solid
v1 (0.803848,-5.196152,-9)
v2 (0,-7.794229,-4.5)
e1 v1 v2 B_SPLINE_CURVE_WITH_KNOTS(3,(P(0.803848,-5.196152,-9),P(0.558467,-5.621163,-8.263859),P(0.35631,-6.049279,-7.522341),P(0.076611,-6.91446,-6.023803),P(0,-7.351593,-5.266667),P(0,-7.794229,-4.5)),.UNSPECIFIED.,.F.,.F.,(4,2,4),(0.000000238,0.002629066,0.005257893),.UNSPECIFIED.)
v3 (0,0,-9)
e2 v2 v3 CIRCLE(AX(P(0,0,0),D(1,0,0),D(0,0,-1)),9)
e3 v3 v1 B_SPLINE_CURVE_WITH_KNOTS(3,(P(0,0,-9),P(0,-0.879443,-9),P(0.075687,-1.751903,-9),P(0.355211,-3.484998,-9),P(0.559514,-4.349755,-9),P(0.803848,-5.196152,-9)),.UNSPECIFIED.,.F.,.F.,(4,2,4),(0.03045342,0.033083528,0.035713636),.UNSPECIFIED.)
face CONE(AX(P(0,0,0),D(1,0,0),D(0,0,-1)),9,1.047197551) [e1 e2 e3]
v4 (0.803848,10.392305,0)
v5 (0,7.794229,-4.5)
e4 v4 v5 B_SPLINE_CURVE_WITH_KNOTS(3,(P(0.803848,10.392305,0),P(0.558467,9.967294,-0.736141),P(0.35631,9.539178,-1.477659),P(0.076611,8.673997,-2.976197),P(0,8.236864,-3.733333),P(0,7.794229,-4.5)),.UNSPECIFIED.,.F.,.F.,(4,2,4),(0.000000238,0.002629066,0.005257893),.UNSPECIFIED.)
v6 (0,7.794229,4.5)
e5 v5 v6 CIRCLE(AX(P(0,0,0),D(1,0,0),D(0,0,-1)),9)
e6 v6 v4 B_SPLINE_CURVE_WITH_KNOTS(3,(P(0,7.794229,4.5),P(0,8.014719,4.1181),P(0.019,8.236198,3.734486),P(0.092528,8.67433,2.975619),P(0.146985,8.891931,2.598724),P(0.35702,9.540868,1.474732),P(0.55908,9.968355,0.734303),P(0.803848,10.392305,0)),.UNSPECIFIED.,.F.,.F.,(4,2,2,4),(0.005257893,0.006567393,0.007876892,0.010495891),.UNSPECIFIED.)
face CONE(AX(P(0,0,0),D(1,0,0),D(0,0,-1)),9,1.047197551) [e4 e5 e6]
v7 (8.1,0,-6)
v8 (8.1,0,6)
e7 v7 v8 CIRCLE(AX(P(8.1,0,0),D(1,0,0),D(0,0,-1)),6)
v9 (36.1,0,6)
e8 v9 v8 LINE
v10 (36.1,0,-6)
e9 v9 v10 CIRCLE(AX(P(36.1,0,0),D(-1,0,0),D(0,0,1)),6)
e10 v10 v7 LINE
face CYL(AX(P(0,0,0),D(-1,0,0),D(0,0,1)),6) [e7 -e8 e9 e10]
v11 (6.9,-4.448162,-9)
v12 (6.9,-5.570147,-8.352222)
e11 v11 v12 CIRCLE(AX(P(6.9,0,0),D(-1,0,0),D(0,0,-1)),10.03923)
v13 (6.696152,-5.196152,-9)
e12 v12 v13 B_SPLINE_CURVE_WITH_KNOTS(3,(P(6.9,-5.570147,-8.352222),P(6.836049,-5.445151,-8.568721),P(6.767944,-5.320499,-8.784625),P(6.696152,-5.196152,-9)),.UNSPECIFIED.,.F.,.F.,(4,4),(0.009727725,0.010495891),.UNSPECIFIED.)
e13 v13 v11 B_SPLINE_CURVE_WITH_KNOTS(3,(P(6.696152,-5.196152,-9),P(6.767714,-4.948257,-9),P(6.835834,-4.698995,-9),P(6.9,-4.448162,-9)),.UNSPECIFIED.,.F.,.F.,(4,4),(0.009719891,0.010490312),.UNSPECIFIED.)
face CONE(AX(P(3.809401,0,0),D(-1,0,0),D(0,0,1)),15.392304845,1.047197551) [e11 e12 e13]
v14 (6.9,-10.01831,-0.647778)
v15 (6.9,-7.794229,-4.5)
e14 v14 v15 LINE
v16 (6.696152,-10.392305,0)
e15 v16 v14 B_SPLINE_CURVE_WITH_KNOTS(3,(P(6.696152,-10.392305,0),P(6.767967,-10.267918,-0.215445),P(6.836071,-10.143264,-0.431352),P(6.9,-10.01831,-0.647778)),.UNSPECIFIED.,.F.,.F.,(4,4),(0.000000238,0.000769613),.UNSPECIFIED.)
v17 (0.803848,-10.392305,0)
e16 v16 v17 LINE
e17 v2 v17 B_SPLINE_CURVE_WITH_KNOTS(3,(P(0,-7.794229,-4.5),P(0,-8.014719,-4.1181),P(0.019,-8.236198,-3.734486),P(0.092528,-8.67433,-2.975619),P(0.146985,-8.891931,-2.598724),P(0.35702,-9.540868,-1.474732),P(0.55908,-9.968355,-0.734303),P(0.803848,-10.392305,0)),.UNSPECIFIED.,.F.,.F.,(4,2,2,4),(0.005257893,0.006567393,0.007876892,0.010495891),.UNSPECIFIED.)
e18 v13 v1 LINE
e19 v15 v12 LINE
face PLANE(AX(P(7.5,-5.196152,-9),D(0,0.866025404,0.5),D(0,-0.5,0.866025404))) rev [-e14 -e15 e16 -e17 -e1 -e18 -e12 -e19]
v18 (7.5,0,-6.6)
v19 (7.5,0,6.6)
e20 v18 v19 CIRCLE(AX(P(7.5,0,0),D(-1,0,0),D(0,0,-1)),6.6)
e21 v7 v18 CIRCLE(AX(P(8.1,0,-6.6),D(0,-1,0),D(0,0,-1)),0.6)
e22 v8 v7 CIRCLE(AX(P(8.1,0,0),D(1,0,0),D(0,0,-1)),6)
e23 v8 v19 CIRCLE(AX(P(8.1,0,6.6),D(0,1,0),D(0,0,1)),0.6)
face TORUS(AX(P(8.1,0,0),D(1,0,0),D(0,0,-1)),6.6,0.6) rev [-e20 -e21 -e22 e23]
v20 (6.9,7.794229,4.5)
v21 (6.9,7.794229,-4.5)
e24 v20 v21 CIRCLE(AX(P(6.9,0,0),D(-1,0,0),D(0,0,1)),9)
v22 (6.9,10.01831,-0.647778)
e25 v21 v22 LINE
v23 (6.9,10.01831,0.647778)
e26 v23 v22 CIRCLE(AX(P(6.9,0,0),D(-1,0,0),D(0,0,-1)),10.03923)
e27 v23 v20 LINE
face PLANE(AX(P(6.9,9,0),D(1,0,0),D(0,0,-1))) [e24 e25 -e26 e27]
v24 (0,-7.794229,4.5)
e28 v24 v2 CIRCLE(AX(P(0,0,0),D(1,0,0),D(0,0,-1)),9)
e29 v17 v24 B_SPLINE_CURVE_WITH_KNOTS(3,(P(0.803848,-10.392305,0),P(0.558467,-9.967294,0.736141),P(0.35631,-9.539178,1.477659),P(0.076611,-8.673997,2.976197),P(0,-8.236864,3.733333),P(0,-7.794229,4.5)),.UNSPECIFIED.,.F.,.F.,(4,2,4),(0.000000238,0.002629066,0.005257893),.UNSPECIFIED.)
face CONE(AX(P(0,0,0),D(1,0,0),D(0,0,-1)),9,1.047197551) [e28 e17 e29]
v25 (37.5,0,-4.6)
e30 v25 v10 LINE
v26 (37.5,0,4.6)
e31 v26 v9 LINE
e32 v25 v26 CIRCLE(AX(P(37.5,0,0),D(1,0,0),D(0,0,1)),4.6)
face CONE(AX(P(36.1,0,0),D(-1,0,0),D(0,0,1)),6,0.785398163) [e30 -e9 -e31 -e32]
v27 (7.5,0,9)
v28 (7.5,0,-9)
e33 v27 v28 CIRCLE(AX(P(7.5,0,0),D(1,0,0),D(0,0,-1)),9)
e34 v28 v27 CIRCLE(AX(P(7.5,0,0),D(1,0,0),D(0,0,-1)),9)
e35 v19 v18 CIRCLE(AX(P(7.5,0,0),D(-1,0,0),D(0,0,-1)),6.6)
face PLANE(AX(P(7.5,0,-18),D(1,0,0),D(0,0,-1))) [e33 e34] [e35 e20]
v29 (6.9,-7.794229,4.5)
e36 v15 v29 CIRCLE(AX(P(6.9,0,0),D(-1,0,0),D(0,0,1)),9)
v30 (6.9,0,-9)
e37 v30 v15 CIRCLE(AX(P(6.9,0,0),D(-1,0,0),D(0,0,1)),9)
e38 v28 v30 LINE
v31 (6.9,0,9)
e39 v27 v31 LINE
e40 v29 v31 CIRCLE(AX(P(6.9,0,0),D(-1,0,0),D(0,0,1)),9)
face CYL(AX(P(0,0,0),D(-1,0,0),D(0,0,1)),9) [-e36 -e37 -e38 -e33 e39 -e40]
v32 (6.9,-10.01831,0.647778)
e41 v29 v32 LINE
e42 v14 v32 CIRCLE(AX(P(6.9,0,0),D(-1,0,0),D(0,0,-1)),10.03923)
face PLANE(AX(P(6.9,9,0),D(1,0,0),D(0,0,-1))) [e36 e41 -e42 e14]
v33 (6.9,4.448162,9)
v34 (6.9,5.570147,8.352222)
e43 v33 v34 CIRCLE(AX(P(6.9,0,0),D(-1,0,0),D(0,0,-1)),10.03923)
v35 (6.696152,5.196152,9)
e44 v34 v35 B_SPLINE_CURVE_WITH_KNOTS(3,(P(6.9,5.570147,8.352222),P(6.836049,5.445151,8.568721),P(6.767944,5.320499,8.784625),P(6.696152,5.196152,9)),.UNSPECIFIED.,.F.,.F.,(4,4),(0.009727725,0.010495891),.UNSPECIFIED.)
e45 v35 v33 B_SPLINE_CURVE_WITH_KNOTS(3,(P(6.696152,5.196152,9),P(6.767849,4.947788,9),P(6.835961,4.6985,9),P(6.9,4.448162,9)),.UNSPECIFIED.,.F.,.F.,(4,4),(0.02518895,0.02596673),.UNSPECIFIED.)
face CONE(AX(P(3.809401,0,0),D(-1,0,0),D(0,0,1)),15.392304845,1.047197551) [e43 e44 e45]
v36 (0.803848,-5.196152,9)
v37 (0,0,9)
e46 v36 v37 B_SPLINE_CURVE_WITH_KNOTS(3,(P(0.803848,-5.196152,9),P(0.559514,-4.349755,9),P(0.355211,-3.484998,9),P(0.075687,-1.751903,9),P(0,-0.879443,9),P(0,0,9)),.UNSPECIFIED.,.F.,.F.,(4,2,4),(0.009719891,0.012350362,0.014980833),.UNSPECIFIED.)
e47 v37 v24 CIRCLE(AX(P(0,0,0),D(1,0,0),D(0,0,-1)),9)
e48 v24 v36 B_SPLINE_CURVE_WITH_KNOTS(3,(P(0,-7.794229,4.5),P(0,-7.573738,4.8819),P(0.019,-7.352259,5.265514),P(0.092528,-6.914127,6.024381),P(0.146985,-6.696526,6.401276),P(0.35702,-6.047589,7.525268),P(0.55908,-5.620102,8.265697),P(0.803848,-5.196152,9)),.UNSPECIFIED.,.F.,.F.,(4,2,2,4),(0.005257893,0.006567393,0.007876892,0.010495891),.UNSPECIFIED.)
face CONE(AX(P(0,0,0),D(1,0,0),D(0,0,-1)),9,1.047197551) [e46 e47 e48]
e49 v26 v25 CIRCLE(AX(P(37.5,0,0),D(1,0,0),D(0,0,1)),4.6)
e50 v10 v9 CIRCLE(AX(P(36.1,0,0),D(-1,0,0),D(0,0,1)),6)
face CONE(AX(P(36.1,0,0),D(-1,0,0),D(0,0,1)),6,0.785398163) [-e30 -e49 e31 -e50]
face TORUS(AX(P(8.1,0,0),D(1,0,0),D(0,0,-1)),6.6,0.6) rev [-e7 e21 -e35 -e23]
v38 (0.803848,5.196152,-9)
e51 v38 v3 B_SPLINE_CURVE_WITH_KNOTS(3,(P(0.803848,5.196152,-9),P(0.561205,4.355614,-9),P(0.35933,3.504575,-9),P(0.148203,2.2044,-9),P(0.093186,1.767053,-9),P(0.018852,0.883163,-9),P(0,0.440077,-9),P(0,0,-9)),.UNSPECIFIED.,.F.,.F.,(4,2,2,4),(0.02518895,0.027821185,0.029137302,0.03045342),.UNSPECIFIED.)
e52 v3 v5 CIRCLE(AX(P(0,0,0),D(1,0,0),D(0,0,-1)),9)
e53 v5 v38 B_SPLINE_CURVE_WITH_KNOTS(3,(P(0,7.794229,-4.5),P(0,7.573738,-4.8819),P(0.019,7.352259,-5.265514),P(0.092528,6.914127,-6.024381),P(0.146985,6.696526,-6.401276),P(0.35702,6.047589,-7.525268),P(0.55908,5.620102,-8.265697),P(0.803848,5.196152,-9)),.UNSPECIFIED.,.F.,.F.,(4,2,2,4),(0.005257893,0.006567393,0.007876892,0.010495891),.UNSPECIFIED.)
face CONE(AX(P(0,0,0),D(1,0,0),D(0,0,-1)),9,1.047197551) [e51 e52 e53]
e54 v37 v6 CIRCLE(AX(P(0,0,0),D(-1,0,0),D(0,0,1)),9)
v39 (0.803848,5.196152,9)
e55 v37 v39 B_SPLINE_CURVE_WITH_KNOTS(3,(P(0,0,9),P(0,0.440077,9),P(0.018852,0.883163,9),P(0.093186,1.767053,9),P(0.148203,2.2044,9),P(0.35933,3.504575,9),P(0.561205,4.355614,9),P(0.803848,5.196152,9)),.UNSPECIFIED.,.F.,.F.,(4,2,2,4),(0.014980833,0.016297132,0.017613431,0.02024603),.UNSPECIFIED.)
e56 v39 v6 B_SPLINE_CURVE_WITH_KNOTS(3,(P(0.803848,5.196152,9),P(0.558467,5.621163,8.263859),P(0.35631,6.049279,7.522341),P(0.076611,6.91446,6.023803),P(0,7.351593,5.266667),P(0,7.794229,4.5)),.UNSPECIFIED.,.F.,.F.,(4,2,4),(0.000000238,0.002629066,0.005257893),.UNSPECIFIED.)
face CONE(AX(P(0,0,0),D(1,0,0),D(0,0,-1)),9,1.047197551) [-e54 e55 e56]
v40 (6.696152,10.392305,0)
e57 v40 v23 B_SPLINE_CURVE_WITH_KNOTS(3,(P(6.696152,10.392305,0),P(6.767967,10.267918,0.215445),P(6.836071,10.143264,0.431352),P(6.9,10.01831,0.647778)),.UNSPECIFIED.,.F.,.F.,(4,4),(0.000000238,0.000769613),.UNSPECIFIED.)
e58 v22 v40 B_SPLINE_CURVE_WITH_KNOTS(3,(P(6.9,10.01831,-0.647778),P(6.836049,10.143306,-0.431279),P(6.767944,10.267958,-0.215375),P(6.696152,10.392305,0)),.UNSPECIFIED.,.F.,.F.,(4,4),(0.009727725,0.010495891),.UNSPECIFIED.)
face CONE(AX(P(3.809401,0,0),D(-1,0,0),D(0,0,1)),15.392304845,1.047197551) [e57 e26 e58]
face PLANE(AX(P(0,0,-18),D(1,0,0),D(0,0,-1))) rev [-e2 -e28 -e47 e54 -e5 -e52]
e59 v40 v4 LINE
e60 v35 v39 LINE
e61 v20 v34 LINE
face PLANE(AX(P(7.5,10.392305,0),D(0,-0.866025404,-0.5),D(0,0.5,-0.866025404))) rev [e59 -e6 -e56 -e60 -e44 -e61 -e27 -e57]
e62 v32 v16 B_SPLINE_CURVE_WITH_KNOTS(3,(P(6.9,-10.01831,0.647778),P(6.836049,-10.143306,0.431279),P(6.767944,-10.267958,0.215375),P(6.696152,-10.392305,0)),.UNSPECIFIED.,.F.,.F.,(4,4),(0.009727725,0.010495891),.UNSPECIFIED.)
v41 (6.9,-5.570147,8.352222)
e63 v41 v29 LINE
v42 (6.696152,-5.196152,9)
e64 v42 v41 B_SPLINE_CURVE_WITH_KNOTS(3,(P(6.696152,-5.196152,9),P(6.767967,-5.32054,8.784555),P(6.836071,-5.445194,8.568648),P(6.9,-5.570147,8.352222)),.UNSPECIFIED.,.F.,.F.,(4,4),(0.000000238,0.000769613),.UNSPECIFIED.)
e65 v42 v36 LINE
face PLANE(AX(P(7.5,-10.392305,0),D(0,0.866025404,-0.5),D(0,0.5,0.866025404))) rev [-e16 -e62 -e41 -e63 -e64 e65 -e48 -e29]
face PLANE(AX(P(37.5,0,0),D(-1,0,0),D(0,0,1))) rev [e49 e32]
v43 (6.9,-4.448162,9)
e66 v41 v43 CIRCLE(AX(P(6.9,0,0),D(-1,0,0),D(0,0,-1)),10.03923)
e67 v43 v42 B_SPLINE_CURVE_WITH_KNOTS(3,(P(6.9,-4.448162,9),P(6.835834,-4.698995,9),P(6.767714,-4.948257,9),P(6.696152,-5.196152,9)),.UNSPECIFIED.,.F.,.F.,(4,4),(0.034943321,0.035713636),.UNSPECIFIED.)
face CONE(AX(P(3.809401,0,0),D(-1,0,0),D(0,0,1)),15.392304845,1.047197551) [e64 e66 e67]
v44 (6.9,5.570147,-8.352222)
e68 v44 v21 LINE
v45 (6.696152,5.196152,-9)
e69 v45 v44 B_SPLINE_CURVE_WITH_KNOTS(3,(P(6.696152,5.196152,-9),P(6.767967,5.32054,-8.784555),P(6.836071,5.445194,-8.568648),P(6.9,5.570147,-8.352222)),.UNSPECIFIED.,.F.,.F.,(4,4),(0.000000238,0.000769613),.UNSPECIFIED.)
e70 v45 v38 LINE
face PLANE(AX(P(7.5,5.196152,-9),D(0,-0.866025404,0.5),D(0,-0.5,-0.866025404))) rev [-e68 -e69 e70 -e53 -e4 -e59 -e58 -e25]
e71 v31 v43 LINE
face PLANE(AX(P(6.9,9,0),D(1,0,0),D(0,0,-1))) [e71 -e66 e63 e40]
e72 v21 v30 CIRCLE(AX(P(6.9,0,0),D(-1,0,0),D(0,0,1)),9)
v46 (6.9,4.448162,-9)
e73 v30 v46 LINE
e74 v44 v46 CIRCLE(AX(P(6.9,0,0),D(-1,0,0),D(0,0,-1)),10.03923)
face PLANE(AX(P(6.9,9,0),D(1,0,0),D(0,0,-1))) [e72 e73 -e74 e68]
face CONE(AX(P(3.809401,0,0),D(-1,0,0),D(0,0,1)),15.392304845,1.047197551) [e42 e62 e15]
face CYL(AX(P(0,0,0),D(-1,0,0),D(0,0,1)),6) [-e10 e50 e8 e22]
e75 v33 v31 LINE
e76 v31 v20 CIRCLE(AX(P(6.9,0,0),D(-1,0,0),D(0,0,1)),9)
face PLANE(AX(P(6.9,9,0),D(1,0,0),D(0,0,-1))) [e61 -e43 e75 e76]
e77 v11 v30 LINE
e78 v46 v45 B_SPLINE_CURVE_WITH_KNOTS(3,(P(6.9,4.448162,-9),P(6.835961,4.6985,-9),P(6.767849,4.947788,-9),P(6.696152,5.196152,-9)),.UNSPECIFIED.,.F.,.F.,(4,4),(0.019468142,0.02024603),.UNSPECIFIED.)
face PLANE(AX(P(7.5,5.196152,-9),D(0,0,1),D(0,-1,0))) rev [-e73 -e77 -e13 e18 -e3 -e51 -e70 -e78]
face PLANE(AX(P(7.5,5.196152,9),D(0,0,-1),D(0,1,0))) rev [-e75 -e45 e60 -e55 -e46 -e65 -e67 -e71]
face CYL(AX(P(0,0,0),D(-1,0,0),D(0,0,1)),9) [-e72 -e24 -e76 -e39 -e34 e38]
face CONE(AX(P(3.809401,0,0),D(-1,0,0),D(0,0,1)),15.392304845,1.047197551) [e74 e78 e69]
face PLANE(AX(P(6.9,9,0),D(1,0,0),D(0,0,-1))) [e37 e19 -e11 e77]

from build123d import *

# Parameters (mm, degrees)
EXTRUDE_368_DEPTH = 7.5
SKETCH_4_W        = 0.6
SKETCH_4_H        = 11.392304845
CHAMFER_1891_SIZE = 1.4
FILLET_1936_R     = 0.6


with BuildPart() as part:
    # 草图1 → Extrude 368 (new body)
    with BuildSketch(Plane(origin=(0, 0, 0), x_dir=(0, 0, -1), z_dir=(1, 0, 0))):
        Polygon((9, 5.196152423), (9, -5.196152423), (0, -10.392304845), (-9, -5.196152423), (-9, 5.196152423), (0, 10.392304845), align=None)
    extrude(amount=EXTRUDE_368_DEPTH)

    # 草图2 → 凸台-旋转1 (revolve)
    with BuildSketch(Plane.XY, mode=Mode.PRIVATE) as revolve_1_sk:
        Polygon((0, 0), (37.5, 0), (37.5, 4.4845), (37.5, 6), (0, 6), align=None)
    revolve(revolve_1_sk.sketch.rotate(Axis((0, 0, 0), (1, 0, 0)), 90), axis=Axis((0, 0, 0), (1, 0, 0)))

    # 草图3 → 切除-旋转1 (revolve, cut)
    with BuildSketch(Plane.XY):
        Polygon((0, 9), (3.690598923, 15.392304845), (3.690598923, 20.392304845), (-10, 20.392304845), (-10, 9), align=None)
    revolve(axis=Axis((0, 0, 0), (1, 0, 0)), mode=Mode.SUBTRACT)

    # 草图5 → 切除-旋转2 (revolve, cut)
    with BuildSketch(Plane.XY):
        Polygon((7.5, 9), (3.809401077, 15.392304845), (3.809401077, 20.392304845), (13.809401077, 20.392304845), (13.809401077, 9), align=None)
    revolve(axis=Axis((0, 0, 0), (1, 0, 0)), mode=Mode.SUBTRACT)

    # 草图4 → 切除-旋转3 (revolve, cut)
    with BuildSketch(Plane.XY, mode=Mode.PRIVATE) as cut_revolve_3_sk:
        with Locations((7.2, 14.696152423)):
            Rectangle(SKETCH_4_W, SKETCH_4_H)
    revolve(cut_revolve_3_sk.sketch.rotate(Axis((0, 0, 0), (1, 0, 0)), 270), axis=Axis((0, 0, 0), (1, 0, 0)), mode=Mode.SUBTRACT)

    # Chamfer 1891
    chamfer_1891_edges = [part.edges().sort_by_distance(p)[0] for p in [
        (37.5, 0, -6),
    ]]
    chamfer(chamfer_1891_edges, length=CHAMFER_1891_SIZE)

    # Fillet 1936
    fillet_1936_edges = [part.edges().sort_by_distance(p)[0] for p in [
        (7.5, 0, -6),
    ]]
    fillet(fillet_1936_edges, radius=FILLET_1936_R)


solid = part.part
